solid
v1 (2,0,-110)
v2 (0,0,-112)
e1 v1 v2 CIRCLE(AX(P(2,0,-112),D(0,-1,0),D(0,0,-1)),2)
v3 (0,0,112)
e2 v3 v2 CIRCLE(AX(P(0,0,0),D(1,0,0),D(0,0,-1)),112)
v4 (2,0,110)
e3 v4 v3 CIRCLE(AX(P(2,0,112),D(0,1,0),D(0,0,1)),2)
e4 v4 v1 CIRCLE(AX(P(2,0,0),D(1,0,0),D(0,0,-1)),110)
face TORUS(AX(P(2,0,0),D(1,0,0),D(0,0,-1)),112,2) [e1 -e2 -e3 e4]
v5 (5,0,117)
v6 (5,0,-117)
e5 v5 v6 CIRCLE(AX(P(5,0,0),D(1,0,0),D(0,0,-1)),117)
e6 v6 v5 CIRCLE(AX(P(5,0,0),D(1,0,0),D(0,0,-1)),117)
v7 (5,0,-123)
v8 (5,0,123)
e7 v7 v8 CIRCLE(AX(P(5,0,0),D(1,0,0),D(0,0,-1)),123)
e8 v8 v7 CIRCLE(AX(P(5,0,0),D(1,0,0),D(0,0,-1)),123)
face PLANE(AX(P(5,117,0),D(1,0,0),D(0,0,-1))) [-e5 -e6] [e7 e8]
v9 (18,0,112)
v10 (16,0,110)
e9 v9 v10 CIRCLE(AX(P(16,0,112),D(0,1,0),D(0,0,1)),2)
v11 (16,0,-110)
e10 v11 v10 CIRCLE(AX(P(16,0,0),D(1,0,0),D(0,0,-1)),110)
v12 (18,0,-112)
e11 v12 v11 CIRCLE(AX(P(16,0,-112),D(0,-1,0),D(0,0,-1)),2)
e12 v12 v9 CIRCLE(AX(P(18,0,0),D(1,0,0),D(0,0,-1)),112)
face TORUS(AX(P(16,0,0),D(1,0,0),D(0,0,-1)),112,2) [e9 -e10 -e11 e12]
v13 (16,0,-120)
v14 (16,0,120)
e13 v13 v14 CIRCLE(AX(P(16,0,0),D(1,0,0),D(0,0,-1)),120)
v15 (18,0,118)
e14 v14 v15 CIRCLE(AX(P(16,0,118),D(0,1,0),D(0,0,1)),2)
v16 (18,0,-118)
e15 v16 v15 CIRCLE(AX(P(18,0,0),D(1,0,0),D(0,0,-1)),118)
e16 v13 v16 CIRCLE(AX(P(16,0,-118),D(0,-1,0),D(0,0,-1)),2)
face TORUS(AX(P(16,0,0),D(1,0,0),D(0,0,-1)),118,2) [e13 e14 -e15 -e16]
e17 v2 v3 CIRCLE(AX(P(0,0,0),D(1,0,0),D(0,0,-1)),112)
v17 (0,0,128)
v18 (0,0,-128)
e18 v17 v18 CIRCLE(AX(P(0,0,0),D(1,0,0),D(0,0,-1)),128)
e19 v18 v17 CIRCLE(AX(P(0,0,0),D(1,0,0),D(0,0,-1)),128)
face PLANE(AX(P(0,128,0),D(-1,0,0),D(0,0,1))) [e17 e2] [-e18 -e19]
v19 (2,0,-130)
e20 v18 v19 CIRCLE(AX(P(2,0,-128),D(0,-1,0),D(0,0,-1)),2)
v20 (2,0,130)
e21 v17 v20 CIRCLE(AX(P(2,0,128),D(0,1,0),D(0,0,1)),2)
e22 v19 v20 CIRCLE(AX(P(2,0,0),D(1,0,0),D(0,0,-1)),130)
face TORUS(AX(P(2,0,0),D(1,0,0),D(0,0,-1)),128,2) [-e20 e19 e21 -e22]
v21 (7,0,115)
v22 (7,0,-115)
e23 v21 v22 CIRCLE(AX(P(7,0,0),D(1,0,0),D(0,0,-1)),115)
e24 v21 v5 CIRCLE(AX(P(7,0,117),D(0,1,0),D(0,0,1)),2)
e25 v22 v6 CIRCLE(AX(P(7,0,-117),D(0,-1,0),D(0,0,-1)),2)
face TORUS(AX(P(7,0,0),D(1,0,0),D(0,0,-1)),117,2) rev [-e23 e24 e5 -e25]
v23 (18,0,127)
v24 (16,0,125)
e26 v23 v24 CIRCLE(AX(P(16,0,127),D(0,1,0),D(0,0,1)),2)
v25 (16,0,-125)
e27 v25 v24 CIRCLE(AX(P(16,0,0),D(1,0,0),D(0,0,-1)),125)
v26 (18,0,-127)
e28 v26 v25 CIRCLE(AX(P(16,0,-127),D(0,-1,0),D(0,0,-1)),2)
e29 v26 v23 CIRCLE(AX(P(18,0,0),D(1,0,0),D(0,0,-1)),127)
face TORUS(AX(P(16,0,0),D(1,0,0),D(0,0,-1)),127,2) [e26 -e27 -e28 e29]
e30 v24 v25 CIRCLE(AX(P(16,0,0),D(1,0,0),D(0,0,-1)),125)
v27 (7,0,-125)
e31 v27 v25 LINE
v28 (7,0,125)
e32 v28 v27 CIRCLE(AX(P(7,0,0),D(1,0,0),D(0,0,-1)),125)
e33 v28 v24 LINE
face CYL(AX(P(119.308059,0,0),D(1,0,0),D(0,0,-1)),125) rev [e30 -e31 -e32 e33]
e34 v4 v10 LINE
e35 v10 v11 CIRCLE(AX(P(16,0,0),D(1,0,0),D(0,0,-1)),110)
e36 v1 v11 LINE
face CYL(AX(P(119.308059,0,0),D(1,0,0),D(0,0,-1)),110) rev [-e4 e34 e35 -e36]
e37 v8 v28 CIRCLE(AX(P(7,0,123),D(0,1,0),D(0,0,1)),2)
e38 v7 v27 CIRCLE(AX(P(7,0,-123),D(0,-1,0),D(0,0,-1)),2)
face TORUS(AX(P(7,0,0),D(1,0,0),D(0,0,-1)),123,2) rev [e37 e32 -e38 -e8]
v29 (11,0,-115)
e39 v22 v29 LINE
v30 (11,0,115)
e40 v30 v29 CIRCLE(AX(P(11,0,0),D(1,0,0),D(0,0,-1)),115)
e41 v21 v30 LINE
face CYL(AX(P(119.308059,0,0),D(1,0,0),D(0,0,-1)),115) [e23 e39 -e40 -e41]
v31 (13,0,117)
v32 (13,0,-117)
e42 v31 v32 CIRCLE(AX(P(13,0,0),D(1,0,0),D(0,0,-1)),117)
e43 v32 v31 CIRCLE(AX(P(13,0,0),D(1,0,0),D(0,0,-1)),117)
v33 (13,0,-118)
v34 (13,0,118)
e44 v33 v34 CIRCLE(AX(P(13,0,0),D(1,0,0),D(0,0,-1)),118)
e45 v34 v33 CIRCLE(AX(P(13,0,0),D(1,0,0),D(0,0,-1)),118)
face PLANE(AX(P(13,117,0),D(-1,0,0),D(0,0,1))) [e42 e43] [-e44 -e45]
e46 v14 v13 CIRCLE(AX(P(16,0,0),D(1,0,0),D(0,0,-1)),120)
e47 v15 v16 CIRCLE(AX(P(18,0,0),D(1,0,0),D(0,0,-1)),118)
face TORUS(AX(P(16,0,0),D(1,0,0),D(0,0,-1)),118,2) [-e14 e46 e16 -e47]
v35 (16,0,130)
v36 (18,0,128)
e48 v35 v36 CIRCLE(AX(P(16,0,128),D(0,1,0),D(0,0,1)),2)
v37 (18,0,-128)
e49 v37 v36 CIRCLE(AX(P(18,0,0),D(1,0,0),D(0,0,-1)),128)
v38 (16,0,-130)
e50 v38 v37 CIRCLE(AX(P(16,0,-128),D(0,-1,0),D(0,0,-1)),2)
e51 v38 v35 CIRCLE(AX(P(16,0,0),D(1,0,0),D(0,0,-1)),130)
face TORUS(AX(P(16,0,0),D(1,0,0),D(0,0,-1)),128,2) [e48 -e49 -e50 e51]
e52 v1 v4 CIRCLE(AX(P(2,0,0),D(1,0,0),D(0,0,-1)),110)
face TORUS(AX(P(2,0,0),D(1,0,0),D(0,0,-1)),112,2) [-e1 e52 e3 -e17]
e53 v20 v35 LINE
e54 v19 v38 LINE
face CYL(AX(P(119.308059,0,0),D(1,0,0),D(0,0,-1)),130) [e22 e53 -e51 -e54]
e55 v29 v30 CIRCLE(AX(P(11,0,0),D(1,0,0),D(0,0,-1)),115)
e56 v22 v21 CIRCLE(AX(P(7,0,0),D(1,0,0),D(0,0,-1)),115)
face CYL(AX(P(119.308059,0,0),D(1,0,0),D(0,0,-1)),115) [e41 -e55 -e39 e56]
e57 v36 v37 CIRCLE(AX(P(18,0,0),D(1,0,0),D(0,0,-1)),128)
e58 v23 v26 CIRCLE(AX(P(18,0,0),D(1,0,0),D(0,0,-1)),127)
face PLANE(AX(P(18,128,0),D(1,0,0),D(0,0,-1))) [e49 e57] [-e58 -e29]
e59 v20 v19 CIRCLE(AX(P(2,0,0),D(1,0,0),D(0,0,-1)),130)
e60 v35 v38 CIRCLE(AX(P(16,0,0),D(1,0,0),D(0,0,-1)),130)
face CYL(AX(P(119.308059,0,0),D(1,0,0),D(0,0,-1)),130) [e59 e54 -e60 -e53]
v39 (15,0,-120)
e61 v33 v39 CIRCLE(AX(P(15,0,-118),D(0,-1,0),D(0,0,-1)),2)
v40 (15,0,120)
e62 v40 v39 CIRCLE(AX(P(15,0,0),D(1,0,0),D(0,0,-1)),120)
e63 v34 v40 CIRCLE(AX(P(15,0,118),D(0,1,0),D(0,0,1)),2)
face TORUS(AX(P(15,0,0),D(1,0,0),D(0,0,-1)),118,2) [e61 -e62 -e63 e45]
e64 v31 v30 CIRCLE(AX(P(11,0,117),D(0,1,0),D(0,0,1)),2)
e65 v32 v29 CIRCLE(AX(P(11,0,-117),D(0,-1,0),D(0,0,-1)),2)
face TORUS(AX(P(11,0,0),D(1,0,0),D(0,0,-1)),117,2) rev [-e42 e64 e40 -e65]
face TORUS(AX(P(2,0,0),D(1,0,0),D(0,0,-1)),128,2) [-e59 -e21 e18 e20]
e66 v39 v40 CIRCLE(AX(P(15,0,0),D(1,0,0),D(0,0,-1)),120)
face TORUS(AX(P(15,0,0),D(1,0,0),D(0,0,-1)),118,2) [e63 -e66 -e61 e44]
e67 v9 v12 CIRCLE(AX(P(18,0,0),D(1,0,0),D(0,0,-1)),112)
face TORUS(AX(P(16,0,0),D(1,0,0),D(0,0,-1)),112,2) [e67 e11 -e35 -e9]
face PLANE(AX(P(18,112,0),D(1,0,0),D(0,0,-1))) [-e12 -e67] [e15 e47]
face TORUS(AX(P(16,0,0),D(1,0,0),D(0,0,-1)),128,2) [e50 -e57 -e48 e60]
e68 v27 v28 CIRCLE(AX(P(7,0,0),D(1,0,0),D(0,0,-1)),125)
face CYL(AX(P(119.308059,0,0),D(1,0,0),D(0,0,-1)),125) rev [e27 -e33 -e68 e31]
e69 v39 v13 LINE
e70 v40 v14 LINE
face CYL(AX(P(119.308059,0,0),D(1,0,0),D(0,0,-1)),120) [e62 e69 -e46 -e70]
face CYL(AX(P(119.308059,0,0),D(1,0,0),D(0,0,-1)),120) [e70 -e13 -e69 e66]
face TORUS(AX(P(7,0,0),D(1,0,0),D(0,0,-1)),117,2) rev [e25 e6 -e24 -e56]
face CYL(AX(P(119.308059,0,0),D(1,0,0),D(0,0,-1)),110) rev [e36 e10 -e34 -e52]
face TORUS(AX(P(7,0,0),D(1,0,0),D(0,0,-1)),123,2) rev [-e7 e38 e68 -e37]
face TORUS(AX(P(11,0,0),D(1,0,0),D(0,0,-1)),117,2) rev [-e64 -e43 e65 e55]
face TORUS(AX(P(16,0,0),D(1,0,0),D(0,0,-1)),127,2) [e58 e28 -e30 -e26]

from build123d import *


with BuildPart() as part:
    # Sketch1 → Revolve1 (revolve)
    with BuildSketch(Plane.XY, mode=Mode.PRIVATE) as revolve1_sk:
        with BuildLine():
            Line((2, 110), (16, 110))
            ThreePointArc((16, 110), (17.414213562, 110.585786438), (18, 112))
            Line((18, 112), (18, 118))
            ThreePointArc((18, 118), (17.414213562, 119.414213562), (16, 120))
            Line((16, 120), (15, 120))
            ThreePointArc((15, 120), (13.585786438, 119.414213562), (13, 118))
            Line((13, 118), (13, 117))
            ThreePointArc((13, 117), (12.414213562, 115.585786438), (11, 115))
            Line((11, 115), (7, 115))
            ThreePointArc((7, 115), (5.585786438, 115.585786438), (5, 117))
            Line((5, 117), (5, 123))
            ThreePointArc((5, 123), (5.585786438, 124.414213562), (7, 125))
            Line((7, 125), (16, 125))
            ThreePointArc((16, 125), (17.414213562, 125.585786438), (18, 127))
            Line((18, 127), (18, 128))
            ThreePointArc((18, 128), (17.414213562, 129.414213562), (16, 130))
            Line((16, 130), (2, 130))
            ThreePointArc((2, 130), (0.585786438, 129.414213562), (0, 128))
            Line((0, 128), (0, 112))
            ThreePointArc((0, 112), (0.585786438, 110.585786438), (2, 110))
        make_face()
    revolve(revolve1_sk.sketch.rotate(Axis((119.308058872, 0, 0), (-1, 0, 0)), 90), axis=Axis((119.308058872, 0, 0), (-1, 0, 0)))


solid = part.part
